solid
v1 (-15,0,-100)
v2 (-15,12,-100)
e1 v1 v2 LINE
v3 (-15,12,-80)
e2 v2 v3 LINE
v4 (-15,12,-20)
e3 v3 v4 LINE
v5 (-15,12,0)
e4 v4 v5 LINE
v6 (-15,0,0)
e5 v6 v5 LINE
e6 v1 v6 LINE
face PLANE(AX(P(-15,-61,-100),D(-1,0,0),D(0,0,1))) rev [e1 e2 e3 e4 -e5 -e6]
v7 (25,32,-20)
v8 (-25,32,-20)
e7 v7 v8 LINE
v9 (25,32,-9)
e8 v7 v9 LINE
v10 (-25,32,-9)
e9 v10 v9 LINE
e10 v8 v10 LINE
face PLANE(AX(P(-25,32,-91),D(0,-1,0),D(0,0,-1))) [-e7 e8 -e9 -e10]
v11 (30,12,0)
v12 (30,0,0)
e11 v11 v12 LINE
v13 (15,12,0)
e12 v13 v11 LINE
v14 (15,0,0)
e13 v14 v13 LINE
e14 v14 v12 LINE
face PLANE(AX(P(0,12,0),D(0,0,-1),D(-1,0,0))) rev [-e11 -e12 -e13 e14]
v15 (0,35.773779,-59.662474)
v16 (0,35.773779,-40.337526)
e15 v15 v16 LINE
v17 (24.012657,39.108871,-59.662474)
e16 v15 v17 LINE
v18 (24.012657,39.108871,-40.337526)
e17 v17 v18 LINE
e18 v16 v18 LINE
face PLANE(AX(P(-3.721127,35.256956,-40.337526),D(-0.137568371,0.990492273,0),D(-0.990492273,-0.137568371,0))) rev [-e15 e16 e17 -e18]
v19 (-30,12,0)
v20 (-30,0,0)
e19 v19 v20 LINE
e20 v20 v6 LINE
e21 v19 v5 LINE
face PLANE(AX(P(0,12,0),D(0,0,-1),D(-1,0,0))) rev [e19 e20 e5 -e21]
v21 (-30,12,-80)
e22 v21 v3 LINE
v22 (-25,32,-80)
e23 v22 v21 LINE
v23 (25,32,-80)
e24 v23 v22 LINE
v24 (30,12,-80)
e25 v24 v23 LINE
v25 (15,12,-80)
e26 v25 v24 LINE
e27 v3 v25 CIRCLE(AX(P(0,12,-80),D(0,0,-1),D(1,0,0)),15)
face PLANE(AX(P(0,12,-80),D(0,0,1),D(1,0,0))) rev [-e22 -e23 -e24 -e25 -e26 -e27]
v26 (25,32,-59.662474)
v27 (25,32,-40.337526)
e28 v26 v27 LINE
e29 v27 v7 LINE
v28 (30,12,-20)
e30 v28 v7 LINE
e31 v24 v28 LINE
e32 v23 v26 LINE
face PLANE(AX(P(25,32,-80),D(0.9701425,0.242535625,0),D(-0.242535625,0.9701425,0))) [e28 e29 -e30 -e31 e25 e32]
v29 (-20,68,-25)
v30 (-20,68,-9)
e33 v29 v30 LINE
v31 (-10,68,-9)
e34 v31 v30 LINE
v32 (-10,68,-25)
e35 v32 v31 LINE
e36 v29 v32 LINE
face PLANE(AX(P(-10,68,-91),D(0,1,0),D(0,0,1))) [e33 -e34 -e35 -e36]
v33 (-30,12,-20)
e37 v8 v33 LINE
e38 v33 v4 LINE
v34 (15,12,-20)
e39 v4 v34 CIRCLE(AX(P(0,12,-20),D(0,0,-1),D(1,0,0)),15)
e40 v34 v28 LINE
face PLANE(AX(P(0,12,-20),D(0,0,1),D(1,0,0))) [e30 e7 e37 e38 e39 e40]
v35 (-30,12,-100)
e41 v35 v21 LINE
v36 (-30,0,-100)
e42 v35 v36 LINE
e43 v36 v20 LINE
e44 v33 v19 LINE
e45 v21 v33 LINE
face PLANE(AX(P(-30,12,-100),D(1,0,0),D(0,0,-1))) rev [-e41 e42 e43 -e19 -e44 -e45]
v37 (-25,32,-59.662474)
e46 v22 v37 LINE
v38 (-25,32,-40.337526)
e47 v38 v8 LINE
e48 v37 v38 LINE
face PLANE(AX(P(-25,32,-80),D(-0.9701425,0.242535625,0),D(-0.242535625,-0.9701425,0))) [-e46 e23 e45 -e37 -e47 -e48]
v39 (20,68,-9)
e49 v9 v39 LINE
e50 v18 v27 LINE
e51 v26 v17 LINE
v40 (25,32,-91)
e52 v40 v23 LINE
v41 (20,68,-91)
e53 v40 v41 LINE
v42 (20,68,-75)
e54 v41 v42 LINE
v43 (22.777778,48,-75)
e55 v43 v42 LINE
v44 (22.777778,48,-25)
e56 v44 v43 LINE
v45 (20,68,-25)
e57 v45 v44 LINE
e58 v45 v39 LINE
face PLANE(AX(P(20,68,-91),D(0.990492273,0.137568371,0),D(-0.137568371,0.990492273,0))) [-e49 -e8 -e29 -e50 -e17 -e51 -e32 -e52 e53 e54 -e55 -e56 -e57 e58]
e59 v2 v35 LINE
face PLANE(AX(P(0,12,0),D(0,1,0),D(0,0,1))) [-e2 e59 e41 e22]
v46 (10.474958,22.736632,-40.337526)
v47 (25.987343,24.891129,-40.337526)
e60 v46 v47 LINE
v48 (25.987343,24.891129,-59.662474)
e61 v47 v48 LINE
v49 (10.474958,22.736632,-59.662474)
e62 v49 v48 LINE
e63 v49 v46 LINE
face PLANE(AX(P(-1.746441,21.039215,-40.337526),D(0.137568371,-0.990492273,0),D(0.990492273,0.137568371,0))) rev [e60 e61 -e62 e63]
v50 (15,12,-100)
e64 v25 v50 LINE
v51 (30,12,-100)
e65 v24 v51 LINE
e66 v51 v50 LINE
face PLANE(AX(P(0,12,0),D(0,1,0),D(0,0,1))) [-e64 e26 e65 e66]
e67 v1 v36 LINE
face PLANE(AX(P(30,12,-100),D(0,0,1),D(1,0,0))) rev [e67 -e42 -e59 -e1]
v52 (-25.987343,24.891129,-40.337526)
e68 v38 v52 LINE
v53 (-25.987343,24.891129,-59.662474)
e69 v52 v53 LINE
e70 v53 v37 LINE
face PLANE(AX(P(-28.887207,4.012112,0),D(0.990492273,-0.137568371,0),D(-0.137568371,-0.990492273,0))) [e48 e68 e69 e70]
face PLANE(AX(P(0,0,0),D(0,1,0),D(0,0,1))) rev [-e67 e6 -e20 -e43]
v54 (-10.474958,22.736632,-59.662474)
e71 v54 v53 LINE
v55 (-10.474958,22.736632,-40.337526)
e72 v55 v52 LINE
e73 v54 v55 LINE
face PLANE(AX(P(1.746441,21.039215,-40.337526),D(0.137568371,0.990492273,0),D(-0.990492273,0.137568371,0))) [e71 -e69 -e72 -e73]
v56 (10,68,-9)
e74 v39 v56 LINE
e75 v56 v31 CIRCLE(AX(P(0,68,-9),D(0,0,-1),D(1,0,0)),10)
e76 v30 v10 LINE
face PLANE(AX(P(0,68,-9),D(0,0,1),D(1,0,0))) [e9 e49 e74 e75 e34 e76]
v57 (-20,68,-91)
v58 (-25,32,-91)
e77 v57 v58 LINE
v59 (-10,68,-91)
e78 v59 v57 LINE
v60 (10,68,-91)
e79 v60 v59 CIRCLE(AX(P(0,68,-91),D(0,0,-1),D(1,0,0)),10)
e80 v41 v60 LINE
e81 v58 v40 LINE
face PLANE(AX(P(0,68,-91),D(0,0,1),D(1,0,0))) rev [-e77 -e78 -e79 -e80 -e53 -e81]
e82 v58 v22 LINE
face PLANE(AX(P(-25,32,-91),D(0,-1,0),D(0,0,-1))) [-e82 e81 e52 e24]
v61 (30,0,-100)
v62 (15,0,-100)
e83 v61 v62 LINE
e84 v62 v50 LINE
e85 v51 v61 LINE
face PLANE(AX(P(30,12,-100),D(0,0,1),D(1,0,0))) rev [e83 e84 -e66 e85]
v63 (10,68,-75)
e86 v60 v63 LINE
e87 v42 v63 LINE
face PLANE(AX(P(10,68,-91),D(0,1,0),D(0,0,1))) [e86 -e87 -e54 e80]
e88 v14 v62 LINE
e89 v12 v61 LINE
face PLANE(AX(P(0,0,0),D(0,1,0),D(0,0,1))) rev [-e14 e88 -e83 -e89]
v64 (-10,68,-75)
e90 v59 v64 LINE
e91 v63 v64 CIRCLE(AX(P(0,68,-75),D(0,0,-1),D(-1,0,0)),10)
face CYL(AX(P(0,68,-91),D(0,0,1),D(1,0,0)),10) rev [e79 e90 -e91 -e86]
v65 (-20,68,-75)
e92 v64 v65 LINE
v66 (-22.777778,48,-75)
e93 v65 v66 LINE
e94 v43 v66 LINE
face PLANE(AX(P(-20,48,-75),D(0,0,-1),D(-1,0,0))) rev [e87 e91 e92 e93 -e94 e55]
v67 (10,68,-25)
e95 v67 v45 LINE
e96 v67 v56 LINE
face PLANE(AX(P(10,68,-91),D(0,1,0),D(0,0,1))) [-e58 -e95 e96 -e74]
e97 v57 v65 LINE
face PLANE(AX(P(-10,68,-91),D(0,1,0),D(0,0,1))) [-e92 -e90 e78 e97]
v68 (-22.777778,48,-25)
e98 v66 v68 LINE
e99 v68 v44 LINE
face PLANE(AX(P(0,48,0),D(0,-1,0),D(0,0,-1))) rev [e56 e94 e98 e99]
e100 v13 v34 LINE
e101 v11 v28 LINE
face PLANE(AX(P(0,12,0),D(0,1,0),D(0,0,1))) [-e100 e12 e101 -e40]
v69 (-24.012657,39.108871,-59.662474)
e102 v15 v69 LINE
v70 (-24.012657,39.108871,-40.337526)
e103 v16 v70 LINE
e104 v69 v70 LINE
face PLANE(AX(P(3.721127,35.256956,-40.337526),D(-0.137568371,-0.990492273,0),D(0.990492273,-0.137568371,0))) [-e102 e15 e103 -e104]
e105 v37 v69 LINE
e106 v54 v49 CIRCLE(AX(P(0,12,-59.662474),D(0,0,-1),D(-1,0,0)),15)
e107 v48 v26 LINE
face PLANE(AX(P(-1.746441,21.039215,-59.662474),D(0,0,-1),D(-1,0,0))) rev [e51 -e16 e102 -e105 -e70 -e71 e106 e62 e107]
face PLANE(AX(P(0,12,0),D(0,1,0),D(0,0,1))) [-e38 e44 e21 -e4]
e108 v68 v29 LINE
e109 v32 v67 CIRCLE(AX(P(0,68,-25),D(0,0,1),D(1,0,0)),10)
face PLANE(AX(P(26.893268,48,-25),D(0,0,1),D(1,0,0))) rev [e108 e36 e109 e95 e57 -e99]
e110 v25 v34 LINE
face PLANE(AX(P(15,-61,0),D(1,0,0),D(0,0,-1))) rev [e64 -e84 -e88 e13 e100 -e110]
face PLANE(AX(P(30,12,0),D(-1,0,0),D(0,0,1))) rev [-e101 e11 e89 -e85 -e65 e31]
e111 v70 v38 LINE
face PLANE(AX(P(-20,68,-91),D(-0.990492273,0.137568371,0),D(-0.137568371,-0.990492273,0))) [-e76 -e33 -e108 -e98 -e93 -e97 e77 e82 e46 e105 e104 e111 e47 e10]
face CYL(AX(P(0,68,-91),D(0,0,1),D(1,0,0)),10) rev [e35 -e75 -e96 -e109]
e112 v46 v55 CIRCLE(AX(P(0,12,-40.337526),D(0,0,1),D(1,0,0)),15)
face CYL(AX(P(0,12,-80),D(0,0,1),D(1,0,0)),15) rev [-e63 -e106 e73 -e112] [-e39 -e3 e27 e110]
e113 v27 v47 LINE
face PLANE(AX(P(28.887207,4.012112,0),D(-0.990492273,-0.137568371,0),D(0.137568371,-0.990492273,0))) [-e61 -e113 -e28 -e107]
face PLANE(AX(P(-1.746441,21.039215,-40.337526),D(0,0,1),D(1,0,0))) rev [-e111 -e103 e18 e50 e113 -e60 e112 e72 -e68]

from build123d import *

# Parameters (mm, degrees)
BASE_BLOCK_DEPTH             = 12
BASE_CHANNEL_CUT_30X15_DEPTH = 73
TAPERED_PEDESTAL_DEPTH       = 60
SADDLE_BODY_DEPTH            = 82
SADDLE_RECESS_CUT_DEPTH      = 20
SIDE_RELIEF_SKETCH_W         = 19.32494716
SIDE_RELIEF_SKETCH_H         = 14.354217055
SIDE_RELIEF_CUT_DEPTH        = 28


with BuildPart() as part:
    # Base Profile Sketch → Base Block (new body)
    with BuildSketch(Plane(origin=(0, 0, 0), x_dir=(1, 0, 0), z_dir=(0, 1, 0))):
        Polygon((0, 0), (30, 0), (30, 100), (-30, 100), (-30, 0), align=None)
    extrude(amount=BASE_BLOCK_DEPTH)

    # Base Channel Sketch → Base Channel Cut 30x15 (cut)
    with BuildSketch(Plane(origin=(0, 12, 0), x_dir=(1, 0, 0), z_dir=(0, 1, 0))):
        Polygon((0, 0), (15, 0), (15, 100), (-15, 100), (-15, 0), align=None)
    extrude(amount=-BASE_CHANNEL_CUT_30X15_DEPTH, mode=Mode.SUBTRACT)


with BuildPart() as base_channel_cut_30x15_piece_1:
    # of the separate pieces the step leaves, piece 1, a body of its own (base_channel_cut_30x15_pieces)
    add(part.part.solids().sort_by_distance((30, 0, 0))[0])



with BuildPart() as base_channel_cut_30x15_piece_2:
    # of the separate pieces the step leaves, piece 2, a body of its own (base_channel_cut_30x15_pieces)
    add(part.part.solids().sort_by_distance((-15, 12, 0))[0])


with BuildPart() as base_channel_cut_30x15_piece_1_1:
    add(base_channel_cut_30x15_piece_1.part)

    add(base_channel_cut_30x15_piece_2.part)  # Tapered Pedestal merges Base Channel Cut 30x15 piece 2
    # Pedestal Profile Sketch → Tapered Pedestal (add)
    with BuildSketch(Plane.XY.offset(-20)):
        with BuildLine():
            Line((0, 32), (25, 32))
            Line((25, 32), (30, 12))
            Line((30, 12), (15, 12))
            ThreePointArc((15, 12), (0, 27), (-15, 12))
            Line((-15, 12), (-30, 12))
            Line((-30, 12), (-25, 32))
            Line((-25, 32), (0, 32))
        make_face()
    extrude(amount=-TAPERED_PEDESTAL_DEPTH)

    # Saddle Profile Sketch → Saddle Body (add)
    with BuildSketch(Plane.XY.offset(-9)):
        with BuildLine():
            Line((10, 68), (20, 68))
            Line((20, 68), (25, 32))
            Line((25, 32), (-10.572876043, 32))
            Line((-10.572876043, 32), (-25, 32))
            Line((-25, 32), (-20, 68))
            Line((-20, 68), (-10, 68))
            ThreePointArc((-10, 68), (0, 58), (10, 68))
        make_face()
    extrude(amount=-SADDLE_BODY_DEPTH)

    # Saddle Recess Sketch → Saddle Recess Cut (cut)
    with BuildSketch(Plane(origin=(0, 68, 0), x_dir=(1, 0, 0), z_dir=(0, 1, 0))):
        Polygon((20, 75), (-20, 75), (-29.513236355, 75), (-29.513236355, 25), (-20, 25), (20, 25), (26.893267856, 25), (26.893267856, 75), align=None)
    extrude(amount=-SADDLE_RECESS_CUT_DEPTH, mode=Mode.SUBTRACT)

    # Side Relief Sketch → Side Relief Cut (cut)
    with BuildSketch(Plane(origin=(28.887206662, 4.012112036, 0), x_dir=(0, 0, -1), z_dir=(0.9904922731777517, 0.13756837127468668, 0))):
        with Locations((50, 28.25654346)):
            Rectangle(SIDE_RELIEF_SKETCH_W, SIDE_RELIEF_SKETCH_H)
    side_relief_cut = extrude(amount=-SIDE_RELIEF_CUT_DEPTH, mode=Mode.SUBTRACT)

    # Side Relief Mirror: Side Relief Cut across plane
    add(side_relief_cut.mirror(Plane(origin=(0, 0, 0), x_dir=(0, 0, 1), z_dir=(1, 0, 0))), mode=Mode.SUBTRACT)


solid = base_channel_cut_30x15_piece_1_1.part
